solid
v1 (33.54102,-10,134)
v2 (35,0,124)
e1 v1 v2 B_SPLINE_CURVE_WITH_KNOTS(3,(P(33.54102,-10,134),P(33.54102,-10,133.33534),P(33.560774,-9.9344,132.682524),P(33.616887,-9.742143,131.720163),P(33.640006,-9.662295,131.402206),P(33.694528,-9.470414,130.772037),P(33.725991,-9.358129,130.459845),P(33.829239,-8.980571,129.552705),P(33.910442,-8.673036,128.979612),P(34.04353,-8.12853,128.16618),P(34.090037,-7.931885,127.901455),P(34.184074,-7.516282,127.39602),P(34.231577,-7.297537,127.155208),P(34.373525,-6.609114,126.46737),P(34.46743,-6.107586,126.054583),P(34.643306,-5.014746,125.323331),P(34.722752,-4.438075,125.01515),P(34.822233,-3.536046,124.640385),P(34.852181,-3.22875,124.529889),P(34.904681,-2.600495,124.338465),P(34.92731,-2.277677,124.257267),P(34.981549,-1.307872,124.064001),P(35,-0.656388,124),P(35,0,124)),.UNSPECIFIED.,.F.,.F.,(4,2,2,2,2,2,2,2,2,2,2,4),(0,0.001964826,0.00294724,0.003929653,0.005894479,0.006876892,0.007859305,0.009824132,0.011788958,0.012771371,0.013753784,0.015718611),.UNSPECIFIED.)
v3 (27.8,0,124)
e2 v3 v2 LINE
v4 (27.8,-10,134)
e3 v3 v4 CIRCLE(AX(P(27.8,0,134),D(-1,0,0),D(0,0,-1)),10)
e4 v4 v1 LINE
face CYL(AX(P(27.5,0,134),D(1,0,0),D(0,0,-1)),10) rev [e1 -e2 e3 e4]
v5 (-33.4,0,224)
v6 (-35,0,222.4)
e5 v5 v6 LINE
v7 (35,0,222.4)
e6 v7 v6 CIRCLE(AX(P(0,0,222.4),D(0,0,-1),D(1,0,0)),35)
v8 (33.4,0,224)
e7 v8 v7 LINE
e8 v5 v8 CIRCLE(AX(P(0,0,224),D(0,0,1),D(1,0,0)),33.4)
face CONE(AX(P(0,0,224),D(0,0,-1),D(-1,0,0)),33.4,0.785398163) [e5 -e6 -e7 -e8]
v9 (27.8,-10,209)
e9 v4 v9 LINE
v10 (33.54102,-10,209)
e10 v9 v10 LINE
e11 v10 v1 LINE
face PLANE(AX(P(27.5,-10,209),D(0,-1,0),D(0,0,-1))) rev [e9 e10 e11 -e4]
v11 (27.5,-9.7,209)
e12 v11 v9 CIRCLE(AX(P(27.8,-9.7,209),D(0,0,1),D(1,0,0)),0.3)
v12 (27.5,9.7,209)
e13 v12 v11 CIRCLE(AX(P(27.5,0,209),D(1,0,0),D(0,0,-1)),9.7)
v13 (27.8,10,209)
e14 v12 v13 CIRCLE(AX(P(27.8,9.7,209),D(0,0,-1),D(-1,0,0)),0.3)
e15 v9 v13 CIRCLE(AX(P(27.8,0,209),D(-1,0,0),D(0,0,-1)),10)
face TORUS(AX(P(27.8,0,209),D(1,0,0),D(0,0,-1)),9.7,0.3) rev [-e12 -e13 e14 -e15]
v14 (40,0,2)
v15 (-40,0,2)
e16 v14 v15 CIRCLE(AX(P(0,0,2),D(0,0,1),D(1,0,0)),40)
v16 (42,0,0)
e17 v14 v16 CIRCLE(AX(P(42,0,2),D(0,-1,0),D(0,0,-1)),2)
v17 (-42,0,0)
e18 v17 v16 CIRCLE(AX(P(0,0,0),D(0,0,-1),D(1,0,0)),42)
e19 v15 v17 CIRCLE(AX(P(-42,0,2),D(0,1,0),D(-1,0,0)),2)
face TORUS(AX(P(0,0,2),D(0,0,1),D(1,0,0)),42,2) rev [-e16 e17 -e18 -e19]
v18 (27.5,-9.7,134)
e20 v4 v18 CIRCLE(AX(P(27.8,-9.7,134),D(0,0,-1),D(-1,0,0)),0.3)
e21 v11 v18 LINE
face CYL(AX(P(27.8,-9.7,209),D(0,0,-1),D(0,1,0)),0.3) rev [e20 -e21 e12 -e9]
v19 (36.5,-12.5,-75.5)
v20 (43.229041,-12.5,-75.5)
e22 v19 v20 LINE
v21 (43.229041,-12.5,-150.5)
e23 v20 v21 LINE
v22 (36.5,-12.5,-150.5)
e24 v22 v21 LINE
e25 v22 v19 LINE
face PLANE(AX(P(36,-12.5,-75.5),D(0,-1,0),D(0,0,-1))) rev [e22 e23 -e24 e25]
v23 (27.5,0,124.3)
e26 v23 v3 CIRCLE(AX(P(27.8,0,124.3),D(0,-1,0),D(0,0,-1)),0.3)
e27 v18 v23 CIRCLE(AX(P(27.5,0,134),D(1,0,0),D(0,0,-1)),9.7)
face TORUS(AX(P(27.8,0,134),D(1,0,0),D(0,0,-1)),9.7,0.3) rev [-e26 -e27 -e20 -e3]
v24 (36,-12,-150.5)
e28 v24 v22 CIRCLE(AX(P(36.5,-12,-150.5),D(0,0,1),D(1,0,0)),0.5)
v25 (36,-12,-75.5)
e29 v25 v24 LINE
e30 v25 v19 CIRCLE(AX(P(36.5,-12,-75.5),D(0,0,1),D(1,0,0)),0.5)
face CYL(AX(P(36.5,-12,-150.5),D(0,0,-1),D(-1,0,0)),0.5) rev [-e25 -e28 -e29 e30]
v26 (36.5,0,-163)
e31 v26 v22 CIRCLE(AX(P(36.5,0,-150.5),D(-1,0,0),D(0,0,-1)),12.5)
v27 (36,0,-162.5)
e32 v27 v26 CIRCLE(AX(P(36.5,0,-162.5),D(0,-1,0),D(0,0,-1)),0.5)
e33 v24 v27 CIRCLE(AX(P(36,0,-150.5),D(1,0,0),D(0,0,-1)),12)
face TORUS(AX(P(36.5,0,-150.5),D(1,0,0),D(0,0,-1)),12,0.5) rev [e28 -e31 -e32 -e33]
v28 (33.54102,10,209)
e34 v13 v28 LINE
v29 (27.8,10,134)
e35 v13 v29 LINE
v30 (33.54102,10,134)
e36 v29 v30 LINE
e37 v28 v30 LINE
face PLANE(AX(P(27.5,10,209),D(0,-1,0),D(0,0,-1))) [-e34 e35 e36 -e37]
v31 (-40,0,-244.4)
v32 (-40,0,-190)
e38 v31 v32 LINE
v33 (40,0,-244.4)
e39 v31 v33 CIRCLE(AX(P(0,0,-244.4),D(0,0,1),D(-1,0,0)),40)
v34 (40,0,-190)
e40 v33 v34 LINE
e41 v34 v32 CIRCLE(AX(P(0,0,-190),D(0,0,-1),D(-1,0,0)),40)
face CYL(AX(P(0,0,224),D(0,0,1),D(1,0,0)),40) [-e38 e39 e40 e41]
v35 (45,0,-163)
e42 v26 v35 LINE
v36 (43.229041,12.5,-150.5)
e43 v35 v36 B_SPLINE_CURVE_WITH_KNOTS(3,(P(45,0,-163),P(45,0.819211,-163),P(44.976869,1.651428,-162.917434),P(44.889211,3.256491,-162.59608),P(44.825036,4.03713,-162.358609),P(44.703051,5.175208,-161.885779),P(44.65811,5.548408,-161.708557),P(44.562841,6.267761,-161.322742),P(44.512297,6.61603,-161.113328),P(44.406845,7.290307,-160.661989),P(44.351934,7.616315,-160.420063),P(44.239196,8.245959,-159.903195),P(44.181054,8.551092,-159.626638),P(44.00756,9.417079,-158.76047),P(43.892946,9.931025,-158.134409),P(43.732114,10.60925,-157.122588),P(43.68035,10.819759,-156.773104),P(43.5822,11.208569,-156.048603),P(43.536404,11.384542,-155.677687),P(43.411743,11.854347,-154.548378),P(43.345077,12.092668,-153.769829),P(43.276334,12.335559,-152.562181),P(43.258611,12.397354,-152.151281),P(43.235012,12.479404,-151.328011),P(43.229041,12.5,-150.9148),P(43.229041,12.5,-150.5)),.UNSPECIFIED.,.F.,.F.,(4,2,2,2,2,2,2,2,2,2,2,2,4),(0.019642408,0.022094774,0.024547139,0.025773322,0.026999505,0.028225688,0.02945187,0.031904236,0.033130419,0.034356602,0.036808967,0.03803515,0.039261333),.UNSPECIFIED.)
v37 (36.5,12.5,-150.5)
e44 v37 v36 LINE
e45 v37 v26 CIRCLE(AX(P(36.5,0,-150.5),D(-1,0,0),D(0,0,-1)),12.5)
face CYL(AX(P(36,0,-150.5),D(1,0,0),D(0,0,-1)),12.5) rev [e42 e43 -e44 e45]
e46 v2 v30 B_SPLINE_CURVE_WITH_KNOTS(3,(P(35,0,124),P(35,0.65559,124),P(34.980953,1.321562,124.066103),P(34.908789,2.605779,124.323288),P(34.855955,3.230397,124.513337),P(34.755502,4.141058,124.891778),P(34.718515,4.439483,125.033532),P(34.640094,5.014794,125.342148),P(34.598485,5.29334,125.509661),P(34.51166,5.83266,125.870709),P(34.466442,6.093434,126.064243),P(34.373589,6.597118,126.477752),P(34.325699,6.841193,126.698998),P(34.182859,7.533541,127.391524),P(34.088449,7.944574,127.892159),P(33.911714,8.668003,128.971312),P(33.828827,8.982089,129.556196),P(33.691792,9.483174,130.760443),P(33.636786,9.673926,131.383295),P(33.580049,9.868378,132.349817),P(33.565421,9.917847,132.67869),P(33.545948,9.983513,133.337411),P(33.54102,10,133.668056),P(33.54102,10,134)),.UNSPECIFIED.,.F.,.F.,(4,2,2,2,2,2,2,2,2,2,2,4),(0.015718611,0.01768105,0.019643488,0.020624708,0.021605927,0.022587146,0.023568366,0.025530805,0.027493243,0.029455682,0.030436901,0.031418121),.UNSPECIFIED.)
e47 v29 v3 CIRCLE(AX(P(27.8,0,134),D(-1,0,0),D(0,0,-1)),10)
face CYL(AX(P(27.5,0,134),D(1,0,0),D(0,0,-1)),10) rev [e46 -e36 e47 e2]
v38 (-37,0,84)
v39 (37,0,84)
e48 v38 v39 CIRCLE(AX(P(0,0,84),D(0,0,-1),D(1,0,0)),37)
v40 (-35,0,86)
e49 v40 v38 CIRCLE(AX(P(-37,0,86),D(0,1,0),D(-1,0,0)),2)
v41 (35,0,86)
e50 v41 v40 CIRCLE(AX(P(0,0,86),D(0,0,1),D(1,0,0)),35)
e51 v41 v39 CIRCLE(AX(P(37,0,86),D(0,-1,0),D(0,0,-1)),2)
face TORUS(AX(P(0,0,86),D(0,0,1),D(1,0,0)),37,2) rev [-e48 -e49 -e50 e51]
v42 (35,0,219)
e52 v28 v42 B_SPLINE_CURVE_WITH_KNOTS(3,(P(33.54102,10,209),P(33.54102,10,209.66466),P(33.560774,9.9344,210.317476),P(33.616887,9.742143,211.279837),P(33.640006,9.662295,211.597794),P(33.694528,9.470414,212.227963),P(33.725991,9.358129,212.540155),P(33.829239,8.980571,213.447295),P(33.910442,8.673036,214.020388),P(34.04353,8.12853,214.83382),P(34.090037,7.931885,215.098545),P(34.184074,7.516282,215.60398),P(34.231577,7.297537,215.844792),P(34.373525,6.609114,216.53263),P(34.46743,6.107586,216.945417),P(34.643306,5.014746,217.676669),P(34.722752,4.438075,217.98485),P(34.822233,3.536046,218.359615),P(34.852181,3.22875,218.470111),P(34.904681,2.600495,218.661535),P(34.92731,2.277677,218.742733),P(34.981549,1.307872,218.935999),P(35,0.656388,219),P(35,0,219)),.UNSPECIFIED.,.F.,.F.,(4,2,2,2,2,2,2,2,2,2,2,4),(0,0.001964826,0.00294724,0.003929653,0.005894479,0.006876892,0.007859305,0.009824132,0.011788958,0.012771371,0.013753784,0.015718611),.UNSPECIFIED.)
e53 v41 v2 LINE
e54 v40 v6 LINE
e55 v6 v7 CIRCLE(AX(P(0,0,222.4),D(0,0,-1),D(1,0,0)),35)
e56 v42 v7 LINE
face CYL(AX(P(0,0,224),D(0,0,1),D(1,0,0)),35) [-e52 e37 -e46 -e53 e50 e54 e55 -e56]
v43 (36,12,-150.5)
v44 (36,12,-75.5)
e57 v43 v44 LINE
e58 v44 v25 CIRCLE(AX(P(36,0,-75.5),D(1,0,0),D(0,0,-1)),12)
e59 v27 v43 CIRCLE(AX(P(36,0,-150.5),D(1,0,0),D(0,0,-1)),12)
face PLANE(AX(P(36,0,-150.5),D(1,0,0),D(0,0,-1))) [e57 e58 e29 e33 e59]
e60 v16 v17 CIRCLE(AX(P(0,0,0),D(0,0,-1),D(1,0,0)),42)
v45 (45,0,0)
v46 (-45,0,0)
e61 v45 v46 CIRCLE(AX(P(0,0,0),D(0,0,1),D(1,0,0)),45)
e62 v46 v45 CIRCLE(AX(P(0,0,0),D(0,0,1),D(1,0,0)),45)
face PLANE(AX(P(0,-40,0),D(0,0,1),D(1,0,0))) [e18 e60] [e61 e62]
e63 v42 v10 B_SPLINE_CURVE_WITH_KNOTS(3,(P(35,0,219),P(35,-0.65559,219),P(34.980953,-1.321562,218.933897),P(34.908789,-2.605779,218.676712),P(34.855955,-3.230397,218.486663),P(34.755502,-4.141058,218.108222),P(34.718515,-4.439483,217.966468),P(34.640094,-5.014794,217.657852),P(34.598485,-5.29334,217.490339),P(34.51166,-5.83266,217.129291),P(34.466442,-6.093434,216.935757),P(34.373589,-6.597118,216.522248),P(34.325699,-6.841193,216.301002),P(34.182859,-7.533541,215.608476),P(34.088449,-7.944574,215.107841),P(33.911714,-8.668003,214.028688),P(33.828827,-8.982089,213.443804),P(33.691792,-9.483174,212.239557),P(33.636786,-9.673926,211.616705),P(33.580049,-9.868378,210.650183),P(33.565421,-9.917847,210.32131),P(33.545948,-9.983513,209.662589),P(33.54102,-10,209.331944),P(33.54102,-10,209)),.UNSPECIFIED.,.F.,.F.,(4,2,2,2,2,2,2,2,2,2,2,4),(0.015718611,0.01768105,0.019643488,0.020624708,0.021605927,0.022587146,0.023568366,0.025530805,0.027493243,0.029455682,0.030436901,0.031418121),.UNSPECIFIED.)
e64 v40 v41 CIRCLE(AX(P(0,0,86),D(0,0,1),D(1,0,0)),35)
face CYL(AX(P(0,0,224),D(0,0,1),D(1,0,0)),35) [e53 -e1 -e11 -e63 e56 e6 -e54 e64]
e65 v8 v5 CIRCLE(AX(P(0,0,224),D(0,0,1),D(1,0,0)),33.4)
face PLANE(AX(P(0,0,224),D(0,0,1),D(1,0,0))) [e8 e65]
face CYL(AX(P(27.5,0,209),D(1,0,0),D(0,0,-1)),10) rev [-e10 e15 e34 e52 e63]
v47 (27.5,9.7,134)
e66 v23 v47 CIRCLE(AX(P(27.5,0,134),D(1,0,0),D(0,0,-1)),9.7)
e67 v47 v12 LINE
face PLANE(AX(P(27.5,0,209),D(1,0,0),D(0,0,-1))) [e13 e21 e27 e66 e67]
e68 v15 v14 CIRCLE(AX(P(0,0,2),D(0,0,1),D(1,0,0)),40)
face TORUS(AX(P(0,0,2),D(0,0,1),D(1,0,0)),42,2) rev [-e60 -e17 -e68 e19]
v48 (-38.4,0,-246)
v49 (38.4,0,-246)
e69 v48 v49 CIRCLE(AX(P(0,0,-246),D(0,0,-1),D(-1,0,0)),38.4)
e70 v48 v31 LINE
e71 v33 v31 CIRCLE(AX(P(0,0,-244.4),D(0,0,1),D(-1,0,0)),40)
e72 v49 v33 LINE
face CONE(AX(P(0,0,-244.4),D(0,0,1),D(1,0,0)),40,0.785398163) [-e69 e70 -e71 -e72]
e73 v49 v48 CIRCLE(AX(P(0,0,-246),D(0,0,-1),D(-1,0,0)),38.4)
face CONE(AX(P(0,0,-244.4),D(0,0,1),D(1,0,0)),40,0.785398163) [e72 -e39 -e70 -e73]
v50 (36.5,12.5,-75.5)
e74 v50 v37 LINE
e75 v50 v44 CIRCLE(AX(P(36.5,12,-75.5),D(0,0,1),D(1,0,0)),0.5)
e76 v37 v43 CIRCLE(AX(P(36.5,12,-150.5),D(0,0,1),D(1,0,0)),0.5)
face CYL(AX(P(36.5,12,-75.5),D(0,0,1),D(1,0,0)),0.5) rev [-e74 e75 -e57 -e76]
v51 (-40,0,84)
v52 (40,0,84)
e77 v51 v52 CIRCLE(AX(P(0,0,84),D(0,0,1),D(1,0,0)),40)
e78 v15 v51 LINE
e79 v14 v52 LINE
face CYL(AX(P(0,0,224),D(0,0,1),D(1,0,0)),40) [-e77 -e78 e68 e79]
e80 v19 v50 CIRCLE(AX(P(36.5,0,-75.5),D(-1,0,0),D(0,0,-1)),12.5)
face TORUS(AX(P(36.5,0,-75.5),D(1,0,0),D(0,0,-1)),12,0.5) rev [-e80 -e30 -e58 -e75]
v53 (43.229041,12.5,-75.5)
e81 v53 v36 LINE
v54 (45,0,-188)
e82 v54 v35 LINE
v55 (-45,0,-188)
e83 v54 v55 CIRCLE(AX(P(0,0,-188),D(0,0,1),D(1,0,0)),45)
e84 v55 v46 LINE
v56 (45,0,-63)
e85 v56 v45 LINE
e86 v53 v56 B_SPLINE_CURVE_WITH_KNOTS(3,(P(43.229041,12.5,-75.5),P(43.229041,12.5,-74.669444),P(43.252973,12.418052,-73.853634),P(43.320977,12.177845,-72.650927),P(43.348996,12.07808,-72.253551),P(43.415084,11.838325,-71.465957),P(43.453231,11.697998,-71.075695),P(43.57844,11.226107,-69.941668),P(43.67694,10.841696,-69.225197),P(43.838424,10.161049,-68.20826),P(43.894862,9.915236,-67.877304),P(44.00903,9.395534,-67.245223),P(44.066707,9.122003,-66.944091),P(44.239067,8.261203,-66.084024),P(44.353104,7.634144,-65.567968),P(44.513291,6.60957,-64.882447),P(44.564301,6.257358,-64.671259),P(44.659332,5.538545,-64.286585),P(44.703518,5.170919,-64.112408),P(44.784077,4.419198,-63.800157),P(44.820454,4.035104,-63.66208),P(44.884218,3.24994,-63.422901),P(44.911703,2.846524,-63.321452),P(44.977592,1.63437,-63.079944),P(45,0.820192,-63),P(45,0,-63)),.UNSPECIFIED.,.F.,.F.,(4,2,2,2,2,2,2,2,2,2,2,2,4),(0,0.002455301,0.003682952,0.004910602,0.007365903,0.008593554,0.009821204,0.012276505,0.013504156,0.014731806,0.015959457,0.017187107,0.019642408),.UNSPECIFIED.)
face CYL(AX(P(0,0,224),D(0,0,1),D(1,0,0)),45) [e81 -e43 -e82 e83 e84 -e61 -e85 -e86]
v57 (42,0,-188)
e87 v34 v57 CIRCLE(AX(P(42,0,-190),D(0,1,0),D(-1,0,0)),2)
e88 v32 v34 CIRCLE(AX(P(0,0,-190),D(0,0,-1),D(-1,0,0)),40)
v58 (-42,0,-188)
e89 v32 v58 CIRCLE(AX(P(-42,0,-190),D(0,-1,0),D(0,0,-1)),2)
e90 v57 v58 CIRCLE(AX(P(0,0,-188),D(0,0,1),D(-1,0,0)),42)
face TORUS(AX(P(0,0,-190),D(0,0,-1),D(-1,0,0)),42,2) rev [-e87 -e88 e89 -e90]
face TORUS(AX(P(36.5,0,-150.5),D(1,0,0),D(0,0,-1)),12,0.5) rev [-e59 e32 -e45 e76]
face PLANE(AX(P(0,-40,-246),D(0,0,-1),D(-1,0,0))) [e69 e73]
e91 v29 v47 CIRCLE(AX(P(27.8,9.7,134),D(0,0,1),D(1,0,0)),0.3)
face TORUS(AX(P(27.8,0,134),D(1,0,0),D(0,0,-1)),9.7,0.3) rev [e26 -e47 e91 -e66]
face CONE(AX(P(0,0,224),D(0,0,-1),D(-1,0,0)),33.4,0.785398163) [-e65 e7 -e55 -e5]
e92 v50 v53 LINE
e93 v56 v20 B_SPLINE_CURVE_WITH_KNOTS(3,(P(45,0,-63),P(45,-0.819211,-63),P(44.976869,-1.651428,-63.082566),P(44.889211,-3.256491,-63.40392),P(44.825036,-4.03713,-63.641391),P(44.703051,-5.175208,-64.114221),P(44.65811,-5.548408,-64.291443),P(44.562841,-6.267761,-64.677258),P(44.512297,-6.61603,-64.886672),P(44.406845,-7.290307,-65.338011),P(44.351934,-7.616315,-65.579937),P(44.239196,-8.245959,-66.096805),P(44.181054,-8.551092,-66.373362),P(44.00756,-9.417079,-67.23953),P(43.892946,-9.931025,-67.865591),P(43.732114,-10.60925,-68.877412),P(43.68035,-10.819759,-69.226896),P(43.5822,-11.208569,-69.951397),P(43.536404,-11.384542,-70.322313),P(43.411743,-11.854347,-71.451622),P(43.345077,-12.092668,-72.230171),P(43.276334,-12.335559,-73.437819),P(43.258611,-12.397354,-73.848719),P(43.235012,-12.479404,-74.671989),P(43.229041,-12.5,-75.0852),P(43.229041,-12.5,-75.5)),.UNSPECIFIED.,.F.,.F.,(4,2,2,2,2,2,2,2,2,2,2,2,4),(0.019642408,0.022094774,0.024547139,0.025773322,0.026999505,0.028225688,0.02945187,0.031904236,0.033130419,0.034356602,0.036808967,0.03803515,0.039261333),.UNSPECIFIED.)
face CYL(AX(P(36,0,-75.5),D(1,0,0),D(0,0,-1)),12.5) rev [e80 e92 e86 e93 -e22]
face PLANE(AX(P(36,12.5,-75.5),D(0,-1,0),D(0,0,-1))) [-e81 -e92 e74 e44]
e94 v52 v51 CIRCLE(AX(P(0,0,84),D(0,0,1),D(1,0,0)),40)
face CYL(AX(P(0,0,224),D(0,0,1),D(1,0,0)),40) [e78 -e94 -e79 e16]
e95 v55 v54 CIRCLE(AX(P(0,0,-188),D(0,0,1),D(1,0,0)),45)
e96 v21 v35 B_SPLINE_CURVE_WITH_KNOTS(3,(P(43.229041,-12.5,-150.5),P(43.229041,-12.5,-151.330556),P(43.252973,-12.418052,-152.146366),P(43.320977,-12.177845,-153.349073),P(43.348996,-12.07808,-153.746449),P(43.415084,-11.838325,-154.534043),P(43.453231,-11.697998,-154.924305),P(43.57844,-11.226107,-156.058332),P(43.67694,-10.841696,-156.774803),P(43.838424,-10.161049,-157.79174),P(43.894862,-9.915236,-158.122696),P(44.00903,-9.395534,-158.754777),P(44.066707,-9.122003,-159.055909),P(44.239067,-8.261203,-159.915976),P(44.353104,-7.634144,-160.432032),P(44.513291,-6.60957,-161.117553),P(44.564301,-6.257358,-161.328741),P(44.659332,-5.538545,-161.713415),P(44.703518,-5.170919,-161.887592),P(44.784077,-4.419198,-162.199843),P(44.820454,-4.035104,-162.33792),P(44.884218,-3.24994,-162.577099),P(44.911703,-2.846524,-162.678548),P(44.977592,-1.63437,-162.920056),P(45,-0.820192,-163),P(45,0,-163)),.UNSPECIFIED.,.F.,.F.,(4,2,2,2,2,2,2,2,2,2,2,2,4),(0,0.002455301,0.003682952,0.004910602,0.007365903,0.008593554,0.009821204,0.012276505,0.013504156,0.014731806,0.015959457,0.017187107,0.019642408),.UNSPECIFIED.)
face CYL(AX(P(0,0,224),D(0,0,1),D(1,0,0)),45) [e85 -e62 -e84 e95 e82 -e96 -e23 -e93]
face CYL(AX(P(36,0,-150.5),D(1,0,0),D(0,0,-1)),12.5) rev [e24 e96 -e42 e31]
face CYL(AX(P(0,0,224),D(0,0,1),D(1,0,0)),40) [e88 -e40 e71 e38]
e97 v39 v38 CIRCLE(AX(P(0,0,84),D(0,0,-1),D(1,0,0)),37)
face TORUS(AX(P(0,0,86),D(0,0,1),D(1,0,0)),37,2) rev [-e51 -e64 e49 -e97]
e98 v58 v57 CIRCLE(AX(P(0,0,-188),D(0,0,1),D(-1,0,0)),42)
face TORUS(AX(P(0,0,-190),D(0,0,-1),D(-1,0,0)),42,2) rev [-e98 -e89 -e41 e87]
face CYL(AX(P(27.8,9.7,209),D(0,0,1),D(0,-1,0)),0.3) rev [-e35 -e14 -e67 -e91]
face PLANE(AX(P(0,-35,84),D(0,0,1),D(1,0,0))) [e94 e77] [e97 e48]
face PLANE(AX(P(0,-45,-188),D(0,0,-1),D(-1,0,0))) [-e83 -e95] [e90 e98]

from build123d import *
from OCP.BRepFilletAPI import BRepFilletAPI_MakeFillet

# Parameters (mm, degrees)
END_CHAMFER_1_6X45_SIZE  = 1.6
SHOULDER_FILLETS_R2_R    = 2
KEYWAY_START             = 35
KEYWAY_1_DEPTH_7_5_DEPTH = 7.5
KEYWAY_START_2           = 45
KEYWAY_2_DEPTH_9_DEPTH   = 9
KEYWAY_EDGE_FILLETS_R1   = 0.3
KEYWAY_EDGE_FILLETS_R2   = 0.5


with BuildPart() as part:
    # Shaft Profile Sketch → Stepped Shaft Body (revolve)
    with BuildSketch(Plane(origin=(0, 0, 0), x_dir=(0, 0, -1), z_dir=(1, 0, 0)), mode=Mode.PRIVATE) as stepped_shaft_body_sk:
        Polygon((-224, 0), (-224, -35), (-84, -35), (-84, -40), (0, -40), (0, -45), (188, -45), (188, -40), (246, -40), (246, 0), align=None)
    revolve(stepped_shaft_body_sk.sketch.rotate(Axis((0, 0, 224), (0, 0, -1)), 270), axis=Axis((0, 0, 224), (0, 0, -1)))

    # End Chamfer 1.6x45
    end_chamfer_1_6x45_edges = [part.edges().sort_by_distance(p)[0] for p in [
        (-35, 0, 224),
        (-40, 0, -246),
    ]]
    chamfer(end_chamfer_1_6x45_edges, length=END_CHAMFER_1_6X45_SIZE)

    # Shoulder Fillets R2
    shoulder_fillets_r2_edges = [part.edges().sort_by_distance(p)[0] for p in [
        (-40, 0, 0),
        (-35, 0, 84),
        (-40, 0, -188),
    ]]
    fillet(shoulder_fillets_r2_edges, radius=SHOULDER_FILLETS_R2_R)

    # Keyway Slots Sketch → Keyway 1 Depth 7.5 (cut)
    with BuildSketch(Plane(origin=(0, 0, 0), x_dir=(0, 0, -1), z_dir=(1, 0, 0)).offset(KEYWAY_START)):
        with BuildLine():
            Line((-209, 10), (-134, 10))
            ThreePointArc((-134, 10), (-124, 0), (-134, -10))
            Line((-134, -10), (-209, -10))
            ThreePointArc((-209, -10), (-219, 0), (-209, 10))
        make_face()
    extrude(amount=-KEYWAY_1_DEPTH_7_5_DEPTH, mode=Mode.SUBTRACT)

    # Sketch2_3 → Keyway 2 Depth 9 (cut)
    with BuildSketch(Plane(origin=(0, 0, 0), x_dir=(0, 0, -1), z_dir=(1, 0, 0)).offset(KEYWAY_START_2)):
        with BuildLine():
            Line((75.5, 12.5), (150.5, 12.5))
            ThreePointArc((150.5, 12.5), (163, 0), (150.5, -12.5))
            Line((150.5, -12.5), (75.5, -12.5))
            ThreePointArc((75.5, -12.5), (63, 0), (75.5, 12.5))
        make_face()
    extrude(amount=-KEYWAY_2_DEPTH_9_DEPTH, mode=Mode.SUBTRACT)

    # Keyway Edge Fillets: one fillet with a radius per group of edges: ONE call of the kernel's fillet builder (fillet() takes one radius for all edges)
    keyway_edge_fillets_edges_1 = [part.edges().sort_by_distance(p)[0] for p in [
        (27.5, 0, 219),
        (27.5, 0, 124),
        (27.5, -10, 171.5),
        (27.5, 10, 171.5),
    ]]
    keyway_edge_fillets_edges_2 = [part.edges().sort_by_distance(p)[0] for p in [
        (36, 0, -163),
        (36, -12.5, -113),
        (36, 0, -63),
        (36, 12.5, -113),
    ]]
    keyway_edge_fillets = BRepFilletAPI_MakeFillet(part.part.solid().wrapped)
    for e in keyway_edge_fillets_edges_1:
        keyway_edge_fillets.Add(KEYWAY_EDGE_FILLETS_R1, e.wrapped)
    for e in keyway_edge_fillets_edges_2:
        keyway_edge_fillets.Add(KEYWAY_EDGE_FILLETS_R2, e.wrapped)
    add(Compound.cast(keyway_edge_fillets.Shape()), mode=Mode.REPLACE)


solid = part.part
